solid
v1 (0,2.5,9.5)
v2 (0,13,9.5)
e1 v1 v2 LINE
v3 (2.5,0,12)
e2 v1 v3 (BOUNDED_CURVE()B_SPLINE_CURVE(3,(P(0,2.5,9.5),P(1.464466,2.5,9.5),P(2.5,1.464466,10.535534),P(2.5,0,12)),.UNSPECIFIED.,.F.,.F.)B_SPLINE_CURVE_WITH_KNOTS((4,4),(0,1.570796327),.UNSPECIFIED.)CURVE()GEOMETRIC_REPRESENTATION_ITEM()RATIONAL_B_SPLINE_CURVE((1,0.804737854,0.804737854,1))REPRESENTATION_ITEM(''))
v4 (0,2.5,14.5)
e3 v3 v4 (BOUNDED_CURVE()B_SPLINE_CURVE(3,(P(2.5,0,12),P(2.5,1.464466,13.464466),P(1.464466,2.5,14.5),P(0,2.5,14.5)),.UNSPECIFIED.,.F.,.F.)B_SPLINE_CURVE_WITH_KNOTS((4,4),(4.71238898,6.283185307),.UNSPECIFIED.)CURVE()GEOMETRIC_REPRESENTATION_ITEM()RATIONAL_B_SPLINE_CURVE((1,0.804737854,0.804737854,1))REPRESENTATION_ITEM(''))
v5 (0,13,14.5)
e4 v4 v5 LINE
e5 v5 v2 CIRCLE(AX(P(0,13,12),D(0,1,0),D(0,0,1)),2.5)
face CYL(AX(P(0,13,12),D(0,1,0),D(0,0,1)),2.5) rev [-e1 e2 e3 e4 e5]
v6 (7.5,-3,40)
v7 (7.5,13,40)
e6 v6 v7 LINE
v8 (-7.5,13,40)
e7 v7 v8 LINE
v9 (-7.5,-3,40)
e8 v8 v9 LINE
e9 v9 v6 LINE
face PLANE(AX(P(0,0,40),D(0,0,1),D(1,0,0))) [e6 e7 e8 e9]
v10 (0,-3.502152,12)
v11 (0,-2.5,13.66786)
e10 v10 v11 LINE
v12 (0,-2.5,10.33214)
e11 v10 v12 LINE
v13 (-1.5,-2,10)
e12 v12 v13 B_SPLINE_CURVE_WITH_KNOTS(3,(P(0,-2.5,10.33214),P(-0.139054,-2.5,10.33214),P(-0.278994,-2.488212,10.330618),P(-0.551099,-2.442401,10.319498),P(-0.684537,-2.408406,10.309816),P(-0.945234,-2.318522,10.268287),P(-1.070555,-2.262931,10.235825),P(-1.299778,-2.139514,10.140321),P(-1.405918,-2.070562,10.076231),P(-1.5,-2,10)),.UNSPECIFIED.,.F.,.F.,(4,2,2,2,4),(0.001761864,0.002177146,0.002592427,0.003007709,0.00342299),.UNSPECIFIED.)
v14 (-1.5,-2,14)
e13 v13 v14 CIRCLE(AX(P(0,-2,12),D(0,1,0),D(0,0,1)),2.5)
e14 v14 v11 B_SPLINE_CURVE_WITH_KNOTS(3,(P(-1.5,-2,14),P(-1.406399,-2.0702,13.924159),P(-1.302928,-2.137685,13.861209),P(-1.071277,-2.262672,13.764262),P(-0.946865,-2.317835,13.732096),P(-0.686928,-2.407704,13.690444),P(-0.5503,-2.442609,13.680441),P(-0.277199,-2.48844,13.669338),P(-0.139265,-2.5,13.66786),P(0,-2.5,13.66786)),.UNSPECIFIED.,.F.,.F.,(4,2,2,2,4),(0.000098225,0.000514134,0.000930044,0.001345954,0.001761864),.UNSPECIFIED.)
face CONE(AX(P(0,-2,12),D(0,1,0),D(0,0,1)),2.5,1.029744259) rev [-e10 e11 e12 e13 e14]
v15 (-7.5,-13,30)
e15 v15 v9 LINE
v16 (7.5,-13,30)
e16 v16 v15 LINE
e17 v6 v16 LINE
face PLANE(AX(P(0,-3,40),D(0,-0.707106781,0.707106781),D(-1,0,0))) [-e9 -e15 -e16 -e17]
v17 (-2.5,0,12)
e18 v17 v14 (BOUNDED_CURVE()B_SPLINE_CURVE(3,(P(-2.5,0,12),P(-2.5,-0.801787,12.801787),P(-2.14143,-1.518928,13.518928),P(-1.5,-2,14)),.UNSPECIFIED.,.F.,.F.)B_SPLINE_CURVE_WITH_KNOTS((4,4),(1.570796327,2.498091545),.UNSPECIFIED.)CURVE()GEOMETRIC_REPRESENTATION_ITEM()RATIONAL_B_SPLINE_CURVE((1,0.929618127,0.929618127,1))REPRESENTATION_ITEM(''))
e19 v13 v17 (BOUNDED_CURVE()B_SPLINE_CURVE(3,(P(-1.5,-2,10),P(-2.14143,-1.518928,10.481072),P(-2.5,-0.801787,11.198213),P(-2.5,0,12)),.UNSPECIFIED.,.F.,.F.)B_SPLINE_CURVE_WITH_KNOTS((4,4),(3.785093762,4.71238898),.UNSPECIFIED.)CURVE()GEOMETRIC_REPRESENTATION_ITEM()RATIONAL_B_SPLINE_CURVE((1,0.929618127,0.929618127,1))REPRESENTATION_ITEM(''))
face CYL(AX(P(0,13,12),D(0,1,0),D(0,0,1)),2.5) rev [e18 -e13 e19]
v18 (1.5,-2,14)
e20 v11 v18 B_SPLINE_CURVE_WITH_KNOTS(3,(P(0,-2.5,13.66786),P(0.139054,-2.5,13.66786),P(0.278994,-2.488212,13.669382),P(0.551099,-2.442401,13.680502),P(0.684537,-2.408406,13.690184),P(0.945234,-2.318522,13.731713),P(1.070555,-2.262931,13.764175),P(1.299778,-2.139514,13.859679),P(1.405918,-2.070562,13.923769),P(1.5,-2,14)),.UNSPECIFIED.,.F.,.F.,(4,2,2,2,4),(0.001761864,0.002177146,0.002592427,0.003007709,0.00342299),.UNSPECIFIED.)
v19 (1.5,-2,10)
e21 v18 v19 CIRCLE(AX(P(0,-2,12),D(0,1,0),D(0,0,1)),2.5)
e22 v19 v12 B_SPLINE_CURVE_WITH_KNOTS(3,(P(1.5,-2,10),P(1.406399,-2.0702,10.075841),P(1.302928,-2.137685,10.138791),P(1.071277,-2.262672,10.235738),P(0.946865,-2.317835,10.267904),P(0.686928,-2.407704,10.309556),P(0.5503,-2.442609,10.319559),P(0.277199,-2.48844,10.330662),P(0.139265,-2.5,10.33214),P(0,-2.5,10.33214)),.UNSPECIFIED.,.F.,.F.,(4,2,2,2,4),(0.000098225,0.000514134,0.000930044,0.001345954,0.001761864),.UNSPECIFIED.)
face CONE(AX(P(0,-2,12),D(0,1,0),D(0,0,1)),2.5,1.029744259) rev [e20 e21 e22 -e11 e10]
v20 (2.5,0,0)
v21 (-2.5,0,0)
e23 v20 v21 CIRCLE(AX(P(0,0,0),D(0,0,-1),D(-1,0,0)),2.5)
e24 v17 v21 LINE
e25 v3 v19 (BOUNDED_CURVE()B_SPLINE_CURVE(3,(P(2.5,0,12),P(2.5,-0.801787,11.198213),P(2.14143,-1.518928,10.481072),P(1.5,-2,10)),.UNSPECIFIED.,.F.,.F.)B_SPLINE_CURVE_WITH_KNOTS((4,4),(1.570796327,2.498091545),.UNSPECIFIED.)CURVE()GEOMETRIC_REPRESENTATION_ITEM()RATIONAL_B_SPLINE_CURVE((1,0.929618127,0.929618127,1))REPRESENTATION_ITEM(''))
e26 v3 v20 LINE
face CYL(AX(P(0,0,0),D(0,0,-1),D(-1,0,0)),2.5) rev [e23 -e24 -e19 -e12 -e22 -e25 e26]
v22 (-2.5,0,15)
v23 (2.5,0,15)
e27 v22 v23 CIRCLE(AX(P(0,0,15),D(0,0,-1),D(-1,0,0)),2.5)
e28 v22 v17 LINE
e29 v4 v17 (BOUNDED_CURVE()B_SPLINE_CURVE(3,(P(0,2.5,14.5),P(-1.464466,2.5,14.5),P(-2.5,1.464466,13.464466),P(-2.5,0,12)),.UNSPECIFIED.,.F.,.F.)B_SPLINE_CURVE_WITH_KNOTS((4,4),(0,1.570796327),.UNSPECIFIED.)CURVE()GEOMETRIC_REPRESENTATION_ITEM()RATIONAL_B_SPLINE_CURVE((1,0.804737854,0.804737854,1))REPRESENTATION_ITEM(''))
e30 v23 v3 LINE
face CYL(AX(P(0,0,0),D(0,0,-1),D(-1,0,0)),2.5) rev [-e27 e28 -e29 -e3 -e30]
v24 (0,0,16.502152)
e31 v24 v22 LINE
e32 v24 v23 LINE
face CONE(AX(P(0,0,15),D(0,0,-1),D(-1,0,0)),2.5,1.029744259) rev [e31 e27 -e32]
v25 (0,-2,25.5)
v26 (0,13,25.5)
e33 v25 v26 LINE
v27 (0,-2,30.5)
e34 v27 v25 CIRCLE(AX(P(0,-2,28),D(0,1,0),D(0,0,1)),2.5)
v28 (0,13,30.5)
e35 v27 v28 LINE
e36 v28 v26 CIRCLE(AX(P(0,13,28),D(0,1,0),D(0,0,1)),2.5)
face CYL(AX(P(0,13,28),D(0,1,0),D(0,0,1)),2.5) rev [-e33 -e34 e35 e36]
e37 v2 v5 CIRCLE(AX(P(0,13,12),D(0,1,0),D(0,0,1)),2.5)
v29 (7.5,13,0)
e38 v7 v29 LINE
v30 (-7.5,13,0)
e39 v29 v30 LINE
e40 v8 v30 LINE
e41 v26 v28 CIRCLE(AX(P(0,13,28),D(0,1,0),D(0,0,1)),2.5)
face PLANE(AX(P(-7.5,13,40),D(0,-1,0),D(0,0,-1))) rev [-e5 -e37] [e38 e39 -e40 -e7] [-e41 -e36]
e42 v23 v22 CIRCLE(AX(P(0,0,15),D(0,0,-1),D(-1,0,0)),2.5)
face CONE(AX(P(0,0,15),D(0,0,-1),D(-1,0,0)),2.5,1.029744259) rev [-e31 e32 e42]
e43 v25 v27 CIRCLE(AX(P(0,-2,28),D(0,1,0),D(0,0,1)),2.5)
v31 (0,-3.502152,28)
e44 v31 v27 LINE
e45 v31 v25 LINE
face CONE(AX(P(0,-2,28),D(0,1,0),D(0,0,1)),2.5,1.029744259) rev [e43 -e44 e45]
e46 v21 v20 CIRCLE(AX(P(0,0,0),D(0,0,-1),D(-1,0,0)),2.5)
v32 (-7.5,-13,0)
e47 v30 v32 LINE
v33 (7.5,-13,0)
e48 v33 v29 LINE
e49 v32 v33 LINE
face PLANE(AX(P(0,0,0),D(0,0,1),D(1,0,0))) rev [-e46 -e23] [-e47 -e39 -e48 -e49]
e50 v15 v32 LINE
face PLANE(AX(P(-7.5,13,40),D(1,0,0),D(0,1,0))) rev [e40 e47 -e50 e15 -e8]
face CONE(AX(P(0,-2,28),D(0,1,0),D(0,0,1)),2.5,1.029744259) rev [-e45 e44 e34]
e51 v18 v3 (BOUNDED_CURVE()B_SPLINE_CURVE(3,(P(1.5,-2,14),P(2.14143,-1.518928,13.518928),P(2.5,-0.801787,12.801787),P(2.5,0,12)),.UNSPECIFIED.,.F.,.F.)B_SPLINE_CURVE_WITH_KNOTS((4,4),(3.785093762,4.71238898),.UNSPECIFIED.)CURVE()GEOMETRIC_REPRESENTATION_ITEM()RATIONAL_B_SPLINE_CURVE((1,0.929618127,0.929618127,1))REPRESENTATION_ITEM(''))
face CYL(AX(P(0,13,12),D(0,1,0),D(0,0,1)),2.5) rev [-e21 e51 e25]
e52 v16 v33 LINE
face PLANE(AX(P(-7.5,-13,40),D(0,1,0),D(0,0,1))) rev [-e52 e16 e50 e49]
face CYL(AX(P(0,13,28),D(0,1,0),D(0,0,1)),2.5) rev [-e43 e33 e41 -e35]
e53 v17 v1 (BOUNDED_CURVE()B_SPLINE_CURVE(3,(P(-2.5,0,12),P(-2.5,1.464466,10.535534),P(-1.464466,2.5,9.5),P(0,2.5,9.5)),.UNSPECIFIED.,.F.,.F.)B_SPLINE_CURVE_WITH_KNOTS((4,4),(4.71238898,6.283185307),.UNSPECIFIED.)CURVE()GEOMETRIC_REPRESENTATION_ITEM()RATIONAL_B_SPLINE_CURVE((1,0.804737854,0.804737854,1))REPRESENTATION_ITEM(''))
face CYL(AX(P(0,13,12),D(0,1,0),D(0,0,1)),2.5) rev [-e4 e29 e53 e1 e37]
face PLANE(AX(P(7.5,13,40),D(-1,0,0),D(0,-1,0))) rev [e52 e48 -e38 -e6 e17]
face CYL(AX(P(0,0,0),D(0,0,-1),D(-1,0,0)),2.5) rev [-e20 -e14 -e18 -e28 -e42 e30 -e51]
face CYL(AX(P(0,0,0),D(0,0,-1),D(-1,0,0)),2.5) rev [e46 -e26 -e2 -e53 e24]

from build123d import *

# Parameters (mm, degrees)
SKETCH_1_W             = 15
SKETCH_1_H             = 26
EXTRUDE_1_DEPTH        = 40
HOLE_WIZARD_M6_1_D     = 5
HOLE_WIZARD_M6_1_DEPTH = 15
HOLE_WIZARD_M6_1_TIP   = 1.502151548
HOLE_WIZARD_M6_2_D     = 5
HOLE_WIZARD_M6_2_DEPTH = 15
HOLE_WIZARD_M6_2_TIP   = 1.502151548
CHAMFER_2_SIZE         = 10


with BuildPart() as part:
    # 草图1 → 凸台-拉伸1 (new body)
    with BuildSketch(Plane.XY):
        Rectangle(SKETCH_1_W, SKETCH_1_H)
    extrude(amount=EXTRUDE_1_DEPTH)

    # M6 螺纹孔1
    with Locations(Plane(origin=(0, 13, 0), x_dir=(1, 0, 0), z_dir=(0, 1, 0))):
        with Locations((0, -12), (0, -28)):
            Hole(HOLE_WIZARD_M6_1_D / 2, depth=HOLE_WIZARD_M6_1_DEPTH)
            with Locations((0, 0, -(HOLE_WIZARD_M6_1_DEPTH + HOLE_WIZARD_M6_1_TIP / 2))):  # 118° drill point
                Cone(0, HOLE_WIZARD_M6_1_D / 2, HOLE_WIZARD_M6_1_TIP, mode=Mode.SUBTRACT)

    # M6 螺纹孔2
    with Locations(Plane(origin=(0, 0, 0), x_dir=(-1, 0, 0), z_dir=(0, 0, -1))):
        with Locations((0, 0)):
            Hole(HOLE_WIZARD_M6_2_D / 2, depth=HOLE_WIZARD_M6_2_DEPTH)
            with Locations((0, 0, -(HOLE_WIZARD_M6_2_DEPTH + HOLE_WIZARD_M6_2_TIP / 2))):  # 118° drill point
                Cone(0, HOLE_WIZARD_M6_2_D / 2, HOLE_WIZARD_M6_2_TIP, mode=Mode.SUBTRACT)

    # 倒角2
    chamfer_2_edges = [part.edges().sort_by_distance(p)[0] for p in [
        (0, -13, 40),
    ]]
    chamfer(chamfer_2_edges, length=CHAMFER_2_SIZE)


solid = part.part
